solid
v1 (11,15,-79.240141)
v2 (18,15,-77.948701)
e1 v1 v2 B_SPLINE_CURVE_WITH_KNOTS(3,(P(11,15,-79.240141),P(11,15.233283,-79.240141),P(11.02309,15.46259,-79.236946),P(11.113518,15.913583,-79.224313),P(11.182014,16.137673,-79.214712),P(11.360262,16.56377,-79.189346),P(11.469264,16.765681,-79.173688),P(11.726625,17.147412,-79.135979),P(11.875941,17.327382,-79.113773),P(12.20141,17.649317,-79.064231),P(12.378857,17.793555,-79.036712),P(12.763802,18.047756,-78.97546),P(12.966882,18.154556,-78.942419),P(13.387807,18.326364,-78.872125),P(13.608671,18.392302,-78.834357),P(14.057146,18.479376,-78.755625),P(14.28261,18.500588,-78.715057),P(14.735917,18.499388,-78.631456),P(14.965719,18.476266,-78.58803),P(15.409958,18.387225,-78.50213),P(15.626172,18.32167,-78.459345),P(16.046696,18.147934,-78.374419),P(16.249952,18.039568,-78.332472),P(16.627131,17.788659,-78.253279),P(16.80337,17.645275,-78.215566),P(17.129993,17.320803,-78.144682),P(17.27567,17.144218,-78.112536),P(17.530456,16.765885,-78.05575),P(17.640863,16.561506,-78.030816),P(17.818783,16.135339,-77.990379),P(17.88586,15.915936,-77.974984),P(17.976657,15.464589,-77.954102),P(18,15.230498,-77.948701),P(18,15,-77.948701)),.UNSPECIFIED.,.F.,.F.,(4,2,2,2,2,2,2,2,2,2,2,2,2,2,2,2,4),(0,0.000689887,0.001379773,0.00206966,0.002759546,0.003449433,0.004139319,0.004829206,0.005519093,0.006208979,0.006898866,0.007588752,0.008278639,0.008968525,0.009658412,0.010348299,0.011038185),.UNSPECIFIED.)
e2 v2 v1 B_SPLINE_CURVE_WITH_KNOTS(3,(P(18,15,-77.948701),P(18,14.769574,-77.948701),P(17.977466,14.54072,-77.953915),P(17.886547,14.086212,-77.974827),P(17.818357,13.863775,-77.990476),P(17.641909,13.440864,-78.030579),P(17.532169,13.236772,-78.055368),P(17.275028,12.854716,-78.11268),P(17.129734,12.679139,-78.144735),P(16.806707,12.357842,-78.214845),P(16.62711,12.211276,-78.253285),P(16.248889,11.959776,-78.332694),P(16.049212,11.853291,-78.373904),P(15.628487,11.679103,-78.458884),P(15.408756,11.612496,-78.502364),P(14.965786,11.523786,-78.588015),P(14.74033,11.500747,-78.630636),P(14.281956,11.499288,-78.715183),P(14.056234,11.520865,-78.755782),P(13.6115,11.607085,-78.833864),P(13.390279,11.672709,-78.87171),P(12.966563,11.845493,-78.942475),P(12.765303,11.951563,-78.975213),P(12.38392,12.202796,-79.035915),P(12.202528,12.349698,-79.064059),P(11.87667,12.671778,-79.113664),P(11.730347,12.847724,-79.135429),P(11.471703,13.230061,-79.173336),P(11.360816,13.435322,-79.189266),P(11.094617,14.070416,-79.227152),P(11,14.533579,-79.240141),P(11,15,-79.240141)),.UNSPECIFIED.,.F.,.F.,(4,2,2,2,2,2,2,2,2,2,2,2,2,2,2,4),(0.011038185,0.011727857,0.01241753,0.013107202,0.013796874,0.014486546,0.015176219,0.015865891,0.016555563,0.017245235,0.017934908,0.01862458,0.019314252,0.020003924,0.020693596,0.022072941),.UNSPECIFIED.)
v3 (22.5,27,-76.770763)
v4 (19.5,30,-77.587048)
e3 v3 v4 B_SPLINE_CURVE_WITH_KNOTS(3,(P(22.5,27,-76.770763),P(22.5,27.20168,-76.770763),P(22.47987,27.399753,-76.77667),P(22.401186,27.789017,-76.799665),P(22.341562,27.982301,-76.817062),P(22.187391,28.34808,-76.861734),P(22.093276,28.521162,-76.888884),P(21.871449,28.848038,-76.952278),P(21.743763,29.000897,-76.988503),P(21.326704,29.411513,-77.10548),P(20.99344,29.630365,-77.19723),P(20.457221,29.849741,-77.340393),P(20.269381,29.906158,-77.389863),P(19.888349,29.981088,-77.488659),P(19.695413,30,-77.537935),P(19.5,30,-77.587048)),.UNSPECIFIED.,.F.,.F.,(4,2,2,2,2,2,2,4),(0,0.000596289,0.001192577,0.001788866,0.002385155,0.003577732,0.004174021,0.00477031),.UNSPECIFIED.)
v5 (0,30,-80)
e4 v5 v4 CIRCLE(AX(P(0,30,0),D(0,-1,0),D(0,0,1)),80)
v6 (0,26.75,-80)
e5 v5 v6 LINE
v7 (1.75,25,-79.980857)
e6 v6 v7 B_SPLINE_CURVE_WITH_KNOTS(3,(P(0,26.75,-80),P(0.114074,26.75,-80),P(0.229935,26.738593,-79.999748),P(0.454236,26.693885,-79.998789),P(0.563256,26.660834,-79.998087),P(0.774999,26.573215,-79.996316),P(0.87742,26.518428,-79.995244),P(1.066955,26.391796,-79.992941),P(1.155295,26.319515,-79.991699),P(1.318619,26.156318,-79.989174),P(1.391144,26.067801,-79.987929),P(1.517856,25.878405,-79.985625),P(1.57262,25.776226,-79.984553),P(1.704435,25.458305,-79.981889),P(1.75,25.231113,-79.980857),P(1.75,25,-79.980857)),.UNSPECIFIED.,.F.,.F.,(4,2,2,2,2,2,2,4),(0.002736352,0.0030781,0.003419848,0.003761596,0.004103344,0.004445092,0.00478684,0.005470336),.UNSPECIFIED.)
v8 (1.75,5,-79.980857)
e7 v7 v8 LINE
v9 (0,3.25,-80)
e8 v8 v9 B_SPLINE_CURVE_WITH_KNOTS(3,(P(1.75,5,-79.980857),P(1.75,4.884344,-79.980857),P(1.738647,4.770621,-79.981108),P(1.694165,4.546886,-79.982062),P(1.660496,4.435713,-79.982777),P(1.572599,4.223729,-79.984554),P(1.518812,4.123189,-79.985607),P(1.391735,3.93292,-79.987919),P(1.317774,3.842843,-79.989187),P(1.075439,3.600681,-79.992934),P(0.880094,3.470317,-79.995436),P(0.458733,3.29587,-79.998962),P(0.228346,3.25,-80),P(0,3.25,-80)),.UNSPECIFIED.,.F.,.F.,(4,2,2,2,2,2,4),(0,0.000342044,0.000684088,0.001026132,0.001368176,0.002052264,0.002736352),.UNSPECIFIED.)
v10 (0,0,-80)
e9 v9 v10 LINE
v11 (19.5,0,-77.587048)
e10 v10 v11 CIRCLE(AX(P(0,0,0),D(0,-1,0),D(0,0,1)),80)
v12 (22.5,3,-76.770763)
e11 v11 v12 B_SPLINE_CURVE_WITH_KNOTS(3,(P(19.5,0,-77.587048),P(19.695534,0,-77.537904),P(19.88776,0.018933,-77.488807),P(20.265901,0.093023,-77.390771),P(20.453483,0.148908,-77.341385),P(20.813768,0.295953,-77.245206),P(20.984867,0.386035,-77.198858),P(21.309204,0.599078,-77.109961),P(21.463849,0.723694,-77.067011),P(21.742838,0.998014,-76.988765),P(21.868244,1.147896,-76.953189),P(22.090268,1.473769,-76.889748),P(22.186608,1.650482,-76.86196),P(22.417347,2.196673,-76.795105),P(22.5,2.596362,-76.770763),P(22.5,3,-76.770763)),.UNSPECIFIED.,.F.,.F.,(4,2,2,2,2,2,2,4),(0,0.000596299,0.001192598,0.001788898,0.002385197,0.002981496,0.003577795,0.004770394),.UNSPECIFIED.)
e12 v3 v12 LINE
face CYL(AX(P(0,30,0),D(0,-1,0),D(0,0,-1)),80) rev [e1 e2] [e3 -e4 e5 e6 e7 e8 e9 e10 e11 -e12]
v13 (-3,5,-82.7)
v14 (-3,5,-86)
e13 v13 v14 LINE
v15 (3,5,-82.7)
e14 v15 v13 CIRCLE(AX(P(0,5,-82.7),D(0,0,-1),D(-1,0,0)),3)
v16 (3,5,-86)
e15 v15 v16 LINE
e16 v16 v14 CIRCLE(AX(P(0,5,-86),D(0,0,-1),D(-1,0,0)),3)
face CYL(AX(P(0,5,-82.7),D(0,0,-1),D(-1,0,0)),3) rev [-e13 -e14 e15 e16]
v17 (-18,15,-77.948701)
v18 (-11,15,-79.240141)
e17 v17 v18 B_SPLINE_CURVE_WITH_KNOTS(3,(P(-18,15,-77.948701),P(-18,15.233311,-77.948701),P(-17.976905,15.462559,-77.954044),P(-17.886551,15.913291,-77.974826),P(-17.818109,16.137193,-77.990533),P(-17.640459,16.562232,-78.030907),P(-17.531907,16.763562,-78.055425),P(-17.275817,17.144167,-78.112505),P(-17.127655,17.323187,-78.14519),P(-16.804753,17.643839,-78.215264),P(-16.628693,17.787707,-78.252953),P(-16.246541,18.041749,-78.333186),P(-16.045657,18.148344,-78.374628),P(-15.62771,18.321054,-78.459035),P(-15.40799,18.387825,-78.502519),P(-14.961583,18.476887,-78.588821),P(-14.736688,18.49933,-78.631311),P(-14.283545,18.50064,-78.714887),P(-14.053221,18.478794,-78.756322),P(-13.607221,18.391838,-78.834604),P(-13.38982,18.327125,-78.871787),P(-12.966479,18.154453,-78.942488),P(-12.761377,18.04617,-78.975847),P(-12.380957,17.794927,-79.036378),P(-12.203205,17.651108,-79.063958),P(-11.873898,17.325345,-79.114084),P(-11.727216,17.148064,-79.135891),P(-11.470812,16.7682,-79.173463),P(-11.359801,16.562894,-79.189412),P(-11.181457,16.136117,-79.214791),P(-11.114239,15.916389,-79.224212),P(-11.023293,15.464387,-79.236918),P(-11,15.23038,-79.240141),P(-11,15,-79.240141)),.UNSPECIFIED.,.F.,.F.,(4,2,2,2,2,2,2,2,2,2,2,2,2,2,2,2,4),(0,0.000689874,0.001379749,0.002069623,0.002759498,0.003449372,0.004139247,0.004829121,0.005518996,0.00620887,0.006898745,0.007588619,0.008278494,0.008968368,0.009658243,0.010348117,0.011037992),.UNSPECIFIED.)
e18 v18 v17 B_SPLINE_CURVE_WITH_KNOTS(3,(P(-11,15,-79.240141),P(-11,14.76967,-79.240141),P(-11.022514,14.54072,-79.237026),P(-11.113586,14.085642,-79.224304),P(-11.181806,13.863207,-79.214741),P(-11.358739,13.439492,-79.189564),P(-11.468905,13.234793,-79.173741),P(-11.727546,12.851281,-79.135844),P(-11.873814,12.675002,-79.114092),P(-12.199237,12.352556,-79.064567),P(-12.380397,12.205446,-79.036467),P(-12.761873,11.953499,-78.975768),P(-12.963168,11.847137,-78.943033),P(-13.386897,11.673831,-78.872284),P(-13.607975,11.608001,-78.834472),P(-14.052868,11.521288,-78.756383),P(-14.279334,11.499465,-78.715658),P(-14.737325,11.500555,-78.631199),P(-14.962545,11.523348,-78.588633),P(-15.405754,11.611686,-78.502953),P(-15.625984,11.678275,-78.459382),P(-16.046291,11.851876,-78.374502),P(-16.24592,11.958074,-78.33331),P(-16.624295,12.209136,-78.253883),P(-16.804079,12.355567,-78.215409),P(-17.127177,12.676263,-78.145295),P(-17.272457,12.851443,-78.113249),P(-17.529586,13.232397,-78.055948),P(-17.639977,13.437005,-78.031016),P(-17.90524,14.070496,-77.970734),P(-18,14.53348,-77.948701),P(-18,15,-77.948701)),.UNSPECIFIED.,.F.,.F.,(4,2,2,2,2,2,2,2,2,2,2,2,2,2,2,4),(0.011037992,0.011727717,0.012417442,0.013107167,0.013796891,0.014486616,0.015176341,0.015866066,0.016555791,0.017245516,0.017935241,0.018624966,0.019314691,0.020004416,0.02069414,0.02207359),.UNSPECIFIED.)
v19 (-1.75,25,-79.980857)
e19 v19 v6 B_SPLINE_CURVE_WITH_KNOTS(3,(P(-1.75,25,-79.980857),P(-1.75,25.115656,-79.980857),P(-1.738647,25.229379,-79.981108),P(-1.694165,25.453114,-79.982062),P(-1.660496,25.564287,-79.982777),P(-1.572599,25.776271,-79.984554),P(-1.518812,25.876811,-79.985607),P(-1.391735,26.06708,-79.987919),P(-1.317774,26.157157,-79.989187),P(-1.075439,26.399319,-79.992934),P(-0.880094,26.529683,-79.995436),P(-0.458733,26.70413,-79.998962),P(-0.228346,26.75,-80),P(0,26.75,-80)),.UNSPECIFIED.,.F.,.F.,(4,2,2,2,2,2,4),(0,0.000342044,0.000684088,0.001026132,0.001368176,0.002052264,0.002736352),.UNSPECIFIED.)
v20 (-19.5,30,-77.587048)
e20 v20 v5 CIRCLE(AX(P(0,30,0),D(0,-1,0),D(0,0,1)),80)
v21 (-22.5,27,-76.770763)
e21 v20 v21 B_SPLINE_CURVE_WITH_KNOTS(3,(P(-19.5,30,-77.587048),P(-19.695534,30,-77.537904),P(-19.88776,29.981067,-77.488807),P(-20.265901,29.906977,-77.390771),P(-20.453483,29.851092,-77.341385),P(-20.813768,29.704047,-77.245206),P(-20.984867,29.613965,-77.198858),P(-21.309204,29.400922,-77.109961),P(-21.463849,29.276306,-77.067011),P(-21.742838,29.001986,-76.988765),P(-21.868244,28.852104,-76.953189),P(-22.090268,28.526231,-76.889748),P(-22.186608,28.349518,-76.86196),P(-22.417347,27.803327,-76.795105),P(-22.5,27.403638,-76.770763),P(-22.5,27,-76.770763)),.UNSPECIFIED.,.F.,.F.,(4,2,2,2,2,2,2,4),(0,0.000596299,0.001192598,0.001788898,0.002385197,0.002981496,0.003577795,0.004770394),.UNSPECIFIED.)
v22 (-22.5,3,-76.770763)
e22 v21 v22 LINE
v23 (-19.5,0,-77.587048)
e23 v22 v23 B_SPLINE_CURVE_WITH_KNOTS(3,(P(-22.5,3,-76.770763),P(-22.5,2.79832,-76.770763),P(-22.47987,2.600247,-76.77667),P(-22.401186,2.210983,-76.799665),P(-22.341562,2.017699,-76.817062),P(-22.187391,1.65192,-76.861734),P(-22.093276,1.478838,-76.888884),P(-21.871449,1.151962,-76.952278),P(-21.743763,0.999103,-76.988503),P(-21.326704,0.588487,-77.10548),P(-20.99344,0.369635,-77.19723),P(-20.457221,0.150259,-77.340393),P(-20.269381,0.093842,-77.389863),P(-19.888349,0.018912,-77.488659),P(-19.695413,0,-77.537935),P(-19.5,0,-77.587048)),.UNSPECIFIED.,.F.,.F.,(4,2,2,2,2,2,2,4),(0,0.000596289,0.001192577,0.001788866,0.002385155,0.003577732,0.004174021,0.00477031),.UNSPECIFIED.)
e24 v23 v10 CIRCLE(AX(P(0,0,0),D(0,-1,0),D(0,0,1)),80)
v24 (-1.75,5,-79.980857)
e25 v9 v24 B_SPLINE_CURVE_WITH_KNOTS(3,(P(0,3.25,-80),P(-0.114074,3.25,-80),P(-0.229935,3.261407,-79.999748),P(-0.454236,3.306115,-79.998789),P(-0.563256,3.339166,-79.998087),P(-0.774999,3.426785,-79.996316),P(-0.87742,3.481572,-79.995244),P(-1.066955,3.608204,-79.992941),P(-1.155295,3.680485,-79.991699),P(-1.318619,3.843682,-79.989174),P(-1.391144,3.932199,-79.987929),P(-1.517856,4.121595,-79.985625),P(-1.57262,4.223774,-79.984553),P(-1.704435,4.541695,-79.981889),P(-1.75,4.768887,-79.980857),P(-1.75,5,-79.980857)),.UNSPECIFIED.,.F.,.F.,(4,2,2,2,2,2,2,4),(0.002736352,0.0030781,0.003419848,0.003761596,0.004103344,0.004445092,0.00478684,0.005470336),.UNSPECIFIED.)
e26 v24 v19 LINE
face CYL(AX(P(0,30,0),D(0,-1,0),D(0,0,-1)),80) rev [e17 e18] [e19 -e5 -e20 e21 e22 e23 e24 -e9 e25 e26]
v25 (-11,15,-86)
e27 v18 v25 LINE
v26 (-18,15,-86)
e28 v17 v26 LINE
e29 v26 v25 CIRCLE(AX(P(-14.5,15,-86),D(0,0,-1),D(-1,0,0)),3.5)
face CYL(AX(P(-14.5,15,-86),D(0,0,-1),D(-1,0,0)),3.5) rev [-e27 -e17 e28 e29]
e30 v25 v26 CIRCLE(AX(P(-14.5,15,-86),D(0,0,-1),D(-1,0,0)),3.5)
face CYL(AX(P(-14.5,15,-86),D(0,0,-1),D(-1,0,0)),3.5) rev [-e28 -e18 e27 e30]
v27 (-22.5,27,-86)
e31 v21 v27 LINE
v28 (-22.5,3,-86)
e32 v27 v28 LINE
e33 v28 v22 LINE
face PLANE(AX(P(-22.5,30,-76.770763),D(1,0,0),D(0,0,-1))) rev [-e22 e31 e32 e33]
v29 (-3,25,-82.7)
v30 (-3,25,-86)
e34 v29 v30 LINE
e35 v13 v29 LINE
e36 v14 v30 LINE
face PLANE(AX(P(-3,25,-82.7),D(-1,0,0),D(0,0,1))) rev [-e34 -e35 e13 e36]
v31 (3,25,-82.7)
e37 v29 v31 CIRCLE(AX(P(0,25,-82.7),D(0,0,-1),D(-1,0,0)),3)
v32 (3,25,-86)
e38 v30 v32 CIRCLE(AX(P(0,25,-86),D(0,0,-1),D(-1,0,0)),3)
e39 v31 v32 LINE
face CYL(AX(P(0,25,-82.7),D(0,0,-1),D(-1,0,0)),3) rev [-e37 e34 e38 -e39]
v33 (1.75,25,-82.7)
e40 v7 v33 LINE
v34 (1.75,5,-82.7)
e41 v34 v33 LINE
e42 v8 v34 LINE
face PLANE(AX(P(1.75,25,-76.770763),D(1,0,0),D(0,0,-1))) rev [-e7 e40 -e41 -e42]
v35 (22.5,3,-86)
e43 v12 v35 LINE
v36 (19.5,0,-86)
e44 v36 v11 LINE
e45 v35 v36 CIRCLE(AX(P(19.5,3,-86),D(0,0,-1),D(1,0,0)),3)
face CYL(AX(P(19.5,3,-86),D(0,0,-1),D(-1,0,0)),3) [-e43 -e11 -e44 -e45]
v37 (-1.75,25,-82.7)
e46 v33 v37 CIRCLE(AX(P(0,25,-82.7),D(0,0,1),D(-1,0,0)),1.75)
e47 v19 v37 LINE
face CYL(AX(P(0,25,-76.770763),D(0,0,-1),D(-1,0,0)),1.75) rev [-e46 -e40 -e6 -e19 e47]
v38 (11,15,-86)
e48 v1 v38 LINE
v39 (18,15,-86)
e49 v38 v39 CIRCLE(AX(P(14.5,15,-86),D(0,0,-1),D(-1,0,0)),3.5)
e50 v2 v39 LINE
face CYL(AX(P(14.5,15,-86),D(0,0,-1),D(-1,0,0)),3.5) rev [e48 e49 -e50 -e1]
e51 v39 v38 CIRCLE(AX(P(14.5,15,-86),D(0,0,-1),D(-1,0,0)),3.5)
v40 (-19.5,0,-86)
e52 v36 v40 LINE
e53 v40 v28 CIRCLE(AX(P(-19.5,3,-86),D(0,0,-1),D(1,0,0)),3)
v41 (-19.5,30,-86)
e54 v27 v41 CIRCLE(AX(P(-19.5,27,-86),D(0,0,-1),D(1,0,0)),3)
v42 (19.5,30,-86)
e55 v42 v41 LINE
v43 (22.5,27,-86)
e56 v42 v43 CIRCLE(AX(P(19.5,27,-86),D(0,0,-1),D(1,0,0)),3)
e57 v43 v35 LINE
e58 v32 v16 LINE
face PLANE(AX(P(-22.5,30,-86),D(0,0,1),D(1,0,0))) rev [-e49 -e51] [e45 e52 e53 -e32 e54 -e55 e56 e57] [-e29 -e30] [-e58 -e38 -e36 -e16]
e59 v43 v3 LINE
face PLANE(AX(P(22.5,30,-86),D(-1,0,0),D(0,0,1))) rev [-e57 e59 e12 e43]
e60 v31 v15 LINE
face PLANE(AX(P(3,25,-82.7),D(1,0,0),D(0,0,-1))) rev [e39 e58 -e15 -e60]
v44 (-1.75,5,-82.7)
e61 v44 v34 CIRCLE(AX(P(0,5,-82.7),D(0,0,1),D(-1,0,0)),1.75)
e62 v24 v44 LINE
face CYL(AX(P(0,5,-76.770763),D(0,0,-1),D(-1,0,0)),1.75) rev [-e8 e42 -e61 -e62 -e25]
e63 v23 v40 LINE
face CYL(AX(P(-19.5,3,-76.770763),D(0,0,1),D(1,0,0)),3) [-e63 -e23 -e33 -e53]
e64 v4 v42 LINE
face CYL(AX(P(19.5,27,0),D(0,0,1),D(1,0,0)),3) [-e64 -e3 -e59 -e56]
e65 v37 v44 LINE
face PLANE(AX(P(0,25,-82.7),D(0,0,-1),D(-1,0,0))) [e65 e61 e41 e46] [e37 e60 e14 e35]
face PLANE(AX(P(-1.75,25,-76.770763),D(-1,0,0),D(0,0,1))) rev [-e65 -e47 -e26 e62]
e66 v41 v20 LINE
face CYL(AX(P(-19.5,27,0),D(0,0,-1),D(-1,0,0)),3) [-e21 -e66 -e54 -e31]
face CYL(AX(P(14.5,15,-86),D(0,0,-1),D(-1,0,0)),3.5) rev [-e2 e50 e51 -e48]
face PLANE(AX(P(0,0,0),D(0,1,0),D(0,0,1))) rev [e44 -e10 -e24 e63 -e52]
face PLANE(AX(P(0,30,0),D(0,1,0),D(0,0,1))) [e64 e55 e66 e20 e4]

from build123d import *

# Parameters (mm, degrees)
BOSS_EXTRUDE1_DEPTH   = 30
M8X1_0_TAPPED_HOLE1_D = 7
CUT_EXTRUDE1_DEPTH    = 39.619021662
CUT_EXTRUDE2_DEPTH    = 3.3
FILLET1_R             = 3


with BuildPart() as part:
    # Sketch1 → Boss-Extrude1 (new body)
    with BuildSketch(Plane(origin=(0, 0, 0), x_dir=(1, 0, 0), z_dir=(0, 1, 0))):
        with BuildLine():
            Line((-22.5, 76.770762664), (-22.5, 86))
            Line((-22.5, 86), (22.5, 86))
            Line((22.5, 86), (22.5, 76.770762664))
            ThreePointArc((22.5, 76.770762664), (0, 80), (-22.5, 76.770762664))
        make_face()
    extrude(amount=BOSS_EXTRUDE1_DEPTH)

    # M8x1.0 Tapped Hole1 (through all)
    with Locations(Plane(origin=(0, 0, -86), x_dir=(-1, 0, 0), z_dir=(0, 0, -1))):
        with Locations((-14.5, 15), (14.5, 15)):
            Hole(M8X1_0_TAPPED_HOLE1_D / 2)

    # Sketch4 → Cut-Extrude1 (cut, through all)
    with BuildSketch(Plane(origin=(0, 0, -86), x_dir=(-1, 0, 0), z_dir=(0, 0, -1))):
        with BuildLine():
            Line((1.75, 25), (1.75, 5))
            ThreePointArc((1.75, 5), (0, 3.25), (-1.75, 5))
            Line((-1.75, 5), (-1.75, 25))
            ThreePointArc((-1.75, 25), (0, 26.75), (1.75, 25))
        make_face()
    extrude(amount=-CUT_EXTRUDE1_DEPTH, mode=Mode.SUBTRACT)

    # Sketch5 → Cut-Extrude2 (cut)
    with BuildSketch(Plane(origin=(0, 0, -86), x_dir=(-1, 0, 0), z_dir=(0, 0, -1))):
        with BuildLine():
            Line((3, 25), (3, 5))
            ThreePointArc((3, 5), (0, 2), (-3, 5))
            Line((-3, 5), (-3, 25))
            ThreePointArc((-3, 25), (0, 28), (3, 25))
        make_face()
    extrude(amount=-CUT_EXTRUDE2_DEPTH, mode=Mode.SUBTRACT)

    # Fillet1
    fillet1_edges = [part.edges().sort_by_distance(p)[0] for p in [
        (22.5, 30, -81.385381332),
        (22.5, 0, -81.385381332),
        (-22.5, 0, -81.385381332),
        (-22.5, 30, -81.385381332),
    ]]
    fillet(fillet1_edges, radius=FILLET1_R)


solid = part.part
